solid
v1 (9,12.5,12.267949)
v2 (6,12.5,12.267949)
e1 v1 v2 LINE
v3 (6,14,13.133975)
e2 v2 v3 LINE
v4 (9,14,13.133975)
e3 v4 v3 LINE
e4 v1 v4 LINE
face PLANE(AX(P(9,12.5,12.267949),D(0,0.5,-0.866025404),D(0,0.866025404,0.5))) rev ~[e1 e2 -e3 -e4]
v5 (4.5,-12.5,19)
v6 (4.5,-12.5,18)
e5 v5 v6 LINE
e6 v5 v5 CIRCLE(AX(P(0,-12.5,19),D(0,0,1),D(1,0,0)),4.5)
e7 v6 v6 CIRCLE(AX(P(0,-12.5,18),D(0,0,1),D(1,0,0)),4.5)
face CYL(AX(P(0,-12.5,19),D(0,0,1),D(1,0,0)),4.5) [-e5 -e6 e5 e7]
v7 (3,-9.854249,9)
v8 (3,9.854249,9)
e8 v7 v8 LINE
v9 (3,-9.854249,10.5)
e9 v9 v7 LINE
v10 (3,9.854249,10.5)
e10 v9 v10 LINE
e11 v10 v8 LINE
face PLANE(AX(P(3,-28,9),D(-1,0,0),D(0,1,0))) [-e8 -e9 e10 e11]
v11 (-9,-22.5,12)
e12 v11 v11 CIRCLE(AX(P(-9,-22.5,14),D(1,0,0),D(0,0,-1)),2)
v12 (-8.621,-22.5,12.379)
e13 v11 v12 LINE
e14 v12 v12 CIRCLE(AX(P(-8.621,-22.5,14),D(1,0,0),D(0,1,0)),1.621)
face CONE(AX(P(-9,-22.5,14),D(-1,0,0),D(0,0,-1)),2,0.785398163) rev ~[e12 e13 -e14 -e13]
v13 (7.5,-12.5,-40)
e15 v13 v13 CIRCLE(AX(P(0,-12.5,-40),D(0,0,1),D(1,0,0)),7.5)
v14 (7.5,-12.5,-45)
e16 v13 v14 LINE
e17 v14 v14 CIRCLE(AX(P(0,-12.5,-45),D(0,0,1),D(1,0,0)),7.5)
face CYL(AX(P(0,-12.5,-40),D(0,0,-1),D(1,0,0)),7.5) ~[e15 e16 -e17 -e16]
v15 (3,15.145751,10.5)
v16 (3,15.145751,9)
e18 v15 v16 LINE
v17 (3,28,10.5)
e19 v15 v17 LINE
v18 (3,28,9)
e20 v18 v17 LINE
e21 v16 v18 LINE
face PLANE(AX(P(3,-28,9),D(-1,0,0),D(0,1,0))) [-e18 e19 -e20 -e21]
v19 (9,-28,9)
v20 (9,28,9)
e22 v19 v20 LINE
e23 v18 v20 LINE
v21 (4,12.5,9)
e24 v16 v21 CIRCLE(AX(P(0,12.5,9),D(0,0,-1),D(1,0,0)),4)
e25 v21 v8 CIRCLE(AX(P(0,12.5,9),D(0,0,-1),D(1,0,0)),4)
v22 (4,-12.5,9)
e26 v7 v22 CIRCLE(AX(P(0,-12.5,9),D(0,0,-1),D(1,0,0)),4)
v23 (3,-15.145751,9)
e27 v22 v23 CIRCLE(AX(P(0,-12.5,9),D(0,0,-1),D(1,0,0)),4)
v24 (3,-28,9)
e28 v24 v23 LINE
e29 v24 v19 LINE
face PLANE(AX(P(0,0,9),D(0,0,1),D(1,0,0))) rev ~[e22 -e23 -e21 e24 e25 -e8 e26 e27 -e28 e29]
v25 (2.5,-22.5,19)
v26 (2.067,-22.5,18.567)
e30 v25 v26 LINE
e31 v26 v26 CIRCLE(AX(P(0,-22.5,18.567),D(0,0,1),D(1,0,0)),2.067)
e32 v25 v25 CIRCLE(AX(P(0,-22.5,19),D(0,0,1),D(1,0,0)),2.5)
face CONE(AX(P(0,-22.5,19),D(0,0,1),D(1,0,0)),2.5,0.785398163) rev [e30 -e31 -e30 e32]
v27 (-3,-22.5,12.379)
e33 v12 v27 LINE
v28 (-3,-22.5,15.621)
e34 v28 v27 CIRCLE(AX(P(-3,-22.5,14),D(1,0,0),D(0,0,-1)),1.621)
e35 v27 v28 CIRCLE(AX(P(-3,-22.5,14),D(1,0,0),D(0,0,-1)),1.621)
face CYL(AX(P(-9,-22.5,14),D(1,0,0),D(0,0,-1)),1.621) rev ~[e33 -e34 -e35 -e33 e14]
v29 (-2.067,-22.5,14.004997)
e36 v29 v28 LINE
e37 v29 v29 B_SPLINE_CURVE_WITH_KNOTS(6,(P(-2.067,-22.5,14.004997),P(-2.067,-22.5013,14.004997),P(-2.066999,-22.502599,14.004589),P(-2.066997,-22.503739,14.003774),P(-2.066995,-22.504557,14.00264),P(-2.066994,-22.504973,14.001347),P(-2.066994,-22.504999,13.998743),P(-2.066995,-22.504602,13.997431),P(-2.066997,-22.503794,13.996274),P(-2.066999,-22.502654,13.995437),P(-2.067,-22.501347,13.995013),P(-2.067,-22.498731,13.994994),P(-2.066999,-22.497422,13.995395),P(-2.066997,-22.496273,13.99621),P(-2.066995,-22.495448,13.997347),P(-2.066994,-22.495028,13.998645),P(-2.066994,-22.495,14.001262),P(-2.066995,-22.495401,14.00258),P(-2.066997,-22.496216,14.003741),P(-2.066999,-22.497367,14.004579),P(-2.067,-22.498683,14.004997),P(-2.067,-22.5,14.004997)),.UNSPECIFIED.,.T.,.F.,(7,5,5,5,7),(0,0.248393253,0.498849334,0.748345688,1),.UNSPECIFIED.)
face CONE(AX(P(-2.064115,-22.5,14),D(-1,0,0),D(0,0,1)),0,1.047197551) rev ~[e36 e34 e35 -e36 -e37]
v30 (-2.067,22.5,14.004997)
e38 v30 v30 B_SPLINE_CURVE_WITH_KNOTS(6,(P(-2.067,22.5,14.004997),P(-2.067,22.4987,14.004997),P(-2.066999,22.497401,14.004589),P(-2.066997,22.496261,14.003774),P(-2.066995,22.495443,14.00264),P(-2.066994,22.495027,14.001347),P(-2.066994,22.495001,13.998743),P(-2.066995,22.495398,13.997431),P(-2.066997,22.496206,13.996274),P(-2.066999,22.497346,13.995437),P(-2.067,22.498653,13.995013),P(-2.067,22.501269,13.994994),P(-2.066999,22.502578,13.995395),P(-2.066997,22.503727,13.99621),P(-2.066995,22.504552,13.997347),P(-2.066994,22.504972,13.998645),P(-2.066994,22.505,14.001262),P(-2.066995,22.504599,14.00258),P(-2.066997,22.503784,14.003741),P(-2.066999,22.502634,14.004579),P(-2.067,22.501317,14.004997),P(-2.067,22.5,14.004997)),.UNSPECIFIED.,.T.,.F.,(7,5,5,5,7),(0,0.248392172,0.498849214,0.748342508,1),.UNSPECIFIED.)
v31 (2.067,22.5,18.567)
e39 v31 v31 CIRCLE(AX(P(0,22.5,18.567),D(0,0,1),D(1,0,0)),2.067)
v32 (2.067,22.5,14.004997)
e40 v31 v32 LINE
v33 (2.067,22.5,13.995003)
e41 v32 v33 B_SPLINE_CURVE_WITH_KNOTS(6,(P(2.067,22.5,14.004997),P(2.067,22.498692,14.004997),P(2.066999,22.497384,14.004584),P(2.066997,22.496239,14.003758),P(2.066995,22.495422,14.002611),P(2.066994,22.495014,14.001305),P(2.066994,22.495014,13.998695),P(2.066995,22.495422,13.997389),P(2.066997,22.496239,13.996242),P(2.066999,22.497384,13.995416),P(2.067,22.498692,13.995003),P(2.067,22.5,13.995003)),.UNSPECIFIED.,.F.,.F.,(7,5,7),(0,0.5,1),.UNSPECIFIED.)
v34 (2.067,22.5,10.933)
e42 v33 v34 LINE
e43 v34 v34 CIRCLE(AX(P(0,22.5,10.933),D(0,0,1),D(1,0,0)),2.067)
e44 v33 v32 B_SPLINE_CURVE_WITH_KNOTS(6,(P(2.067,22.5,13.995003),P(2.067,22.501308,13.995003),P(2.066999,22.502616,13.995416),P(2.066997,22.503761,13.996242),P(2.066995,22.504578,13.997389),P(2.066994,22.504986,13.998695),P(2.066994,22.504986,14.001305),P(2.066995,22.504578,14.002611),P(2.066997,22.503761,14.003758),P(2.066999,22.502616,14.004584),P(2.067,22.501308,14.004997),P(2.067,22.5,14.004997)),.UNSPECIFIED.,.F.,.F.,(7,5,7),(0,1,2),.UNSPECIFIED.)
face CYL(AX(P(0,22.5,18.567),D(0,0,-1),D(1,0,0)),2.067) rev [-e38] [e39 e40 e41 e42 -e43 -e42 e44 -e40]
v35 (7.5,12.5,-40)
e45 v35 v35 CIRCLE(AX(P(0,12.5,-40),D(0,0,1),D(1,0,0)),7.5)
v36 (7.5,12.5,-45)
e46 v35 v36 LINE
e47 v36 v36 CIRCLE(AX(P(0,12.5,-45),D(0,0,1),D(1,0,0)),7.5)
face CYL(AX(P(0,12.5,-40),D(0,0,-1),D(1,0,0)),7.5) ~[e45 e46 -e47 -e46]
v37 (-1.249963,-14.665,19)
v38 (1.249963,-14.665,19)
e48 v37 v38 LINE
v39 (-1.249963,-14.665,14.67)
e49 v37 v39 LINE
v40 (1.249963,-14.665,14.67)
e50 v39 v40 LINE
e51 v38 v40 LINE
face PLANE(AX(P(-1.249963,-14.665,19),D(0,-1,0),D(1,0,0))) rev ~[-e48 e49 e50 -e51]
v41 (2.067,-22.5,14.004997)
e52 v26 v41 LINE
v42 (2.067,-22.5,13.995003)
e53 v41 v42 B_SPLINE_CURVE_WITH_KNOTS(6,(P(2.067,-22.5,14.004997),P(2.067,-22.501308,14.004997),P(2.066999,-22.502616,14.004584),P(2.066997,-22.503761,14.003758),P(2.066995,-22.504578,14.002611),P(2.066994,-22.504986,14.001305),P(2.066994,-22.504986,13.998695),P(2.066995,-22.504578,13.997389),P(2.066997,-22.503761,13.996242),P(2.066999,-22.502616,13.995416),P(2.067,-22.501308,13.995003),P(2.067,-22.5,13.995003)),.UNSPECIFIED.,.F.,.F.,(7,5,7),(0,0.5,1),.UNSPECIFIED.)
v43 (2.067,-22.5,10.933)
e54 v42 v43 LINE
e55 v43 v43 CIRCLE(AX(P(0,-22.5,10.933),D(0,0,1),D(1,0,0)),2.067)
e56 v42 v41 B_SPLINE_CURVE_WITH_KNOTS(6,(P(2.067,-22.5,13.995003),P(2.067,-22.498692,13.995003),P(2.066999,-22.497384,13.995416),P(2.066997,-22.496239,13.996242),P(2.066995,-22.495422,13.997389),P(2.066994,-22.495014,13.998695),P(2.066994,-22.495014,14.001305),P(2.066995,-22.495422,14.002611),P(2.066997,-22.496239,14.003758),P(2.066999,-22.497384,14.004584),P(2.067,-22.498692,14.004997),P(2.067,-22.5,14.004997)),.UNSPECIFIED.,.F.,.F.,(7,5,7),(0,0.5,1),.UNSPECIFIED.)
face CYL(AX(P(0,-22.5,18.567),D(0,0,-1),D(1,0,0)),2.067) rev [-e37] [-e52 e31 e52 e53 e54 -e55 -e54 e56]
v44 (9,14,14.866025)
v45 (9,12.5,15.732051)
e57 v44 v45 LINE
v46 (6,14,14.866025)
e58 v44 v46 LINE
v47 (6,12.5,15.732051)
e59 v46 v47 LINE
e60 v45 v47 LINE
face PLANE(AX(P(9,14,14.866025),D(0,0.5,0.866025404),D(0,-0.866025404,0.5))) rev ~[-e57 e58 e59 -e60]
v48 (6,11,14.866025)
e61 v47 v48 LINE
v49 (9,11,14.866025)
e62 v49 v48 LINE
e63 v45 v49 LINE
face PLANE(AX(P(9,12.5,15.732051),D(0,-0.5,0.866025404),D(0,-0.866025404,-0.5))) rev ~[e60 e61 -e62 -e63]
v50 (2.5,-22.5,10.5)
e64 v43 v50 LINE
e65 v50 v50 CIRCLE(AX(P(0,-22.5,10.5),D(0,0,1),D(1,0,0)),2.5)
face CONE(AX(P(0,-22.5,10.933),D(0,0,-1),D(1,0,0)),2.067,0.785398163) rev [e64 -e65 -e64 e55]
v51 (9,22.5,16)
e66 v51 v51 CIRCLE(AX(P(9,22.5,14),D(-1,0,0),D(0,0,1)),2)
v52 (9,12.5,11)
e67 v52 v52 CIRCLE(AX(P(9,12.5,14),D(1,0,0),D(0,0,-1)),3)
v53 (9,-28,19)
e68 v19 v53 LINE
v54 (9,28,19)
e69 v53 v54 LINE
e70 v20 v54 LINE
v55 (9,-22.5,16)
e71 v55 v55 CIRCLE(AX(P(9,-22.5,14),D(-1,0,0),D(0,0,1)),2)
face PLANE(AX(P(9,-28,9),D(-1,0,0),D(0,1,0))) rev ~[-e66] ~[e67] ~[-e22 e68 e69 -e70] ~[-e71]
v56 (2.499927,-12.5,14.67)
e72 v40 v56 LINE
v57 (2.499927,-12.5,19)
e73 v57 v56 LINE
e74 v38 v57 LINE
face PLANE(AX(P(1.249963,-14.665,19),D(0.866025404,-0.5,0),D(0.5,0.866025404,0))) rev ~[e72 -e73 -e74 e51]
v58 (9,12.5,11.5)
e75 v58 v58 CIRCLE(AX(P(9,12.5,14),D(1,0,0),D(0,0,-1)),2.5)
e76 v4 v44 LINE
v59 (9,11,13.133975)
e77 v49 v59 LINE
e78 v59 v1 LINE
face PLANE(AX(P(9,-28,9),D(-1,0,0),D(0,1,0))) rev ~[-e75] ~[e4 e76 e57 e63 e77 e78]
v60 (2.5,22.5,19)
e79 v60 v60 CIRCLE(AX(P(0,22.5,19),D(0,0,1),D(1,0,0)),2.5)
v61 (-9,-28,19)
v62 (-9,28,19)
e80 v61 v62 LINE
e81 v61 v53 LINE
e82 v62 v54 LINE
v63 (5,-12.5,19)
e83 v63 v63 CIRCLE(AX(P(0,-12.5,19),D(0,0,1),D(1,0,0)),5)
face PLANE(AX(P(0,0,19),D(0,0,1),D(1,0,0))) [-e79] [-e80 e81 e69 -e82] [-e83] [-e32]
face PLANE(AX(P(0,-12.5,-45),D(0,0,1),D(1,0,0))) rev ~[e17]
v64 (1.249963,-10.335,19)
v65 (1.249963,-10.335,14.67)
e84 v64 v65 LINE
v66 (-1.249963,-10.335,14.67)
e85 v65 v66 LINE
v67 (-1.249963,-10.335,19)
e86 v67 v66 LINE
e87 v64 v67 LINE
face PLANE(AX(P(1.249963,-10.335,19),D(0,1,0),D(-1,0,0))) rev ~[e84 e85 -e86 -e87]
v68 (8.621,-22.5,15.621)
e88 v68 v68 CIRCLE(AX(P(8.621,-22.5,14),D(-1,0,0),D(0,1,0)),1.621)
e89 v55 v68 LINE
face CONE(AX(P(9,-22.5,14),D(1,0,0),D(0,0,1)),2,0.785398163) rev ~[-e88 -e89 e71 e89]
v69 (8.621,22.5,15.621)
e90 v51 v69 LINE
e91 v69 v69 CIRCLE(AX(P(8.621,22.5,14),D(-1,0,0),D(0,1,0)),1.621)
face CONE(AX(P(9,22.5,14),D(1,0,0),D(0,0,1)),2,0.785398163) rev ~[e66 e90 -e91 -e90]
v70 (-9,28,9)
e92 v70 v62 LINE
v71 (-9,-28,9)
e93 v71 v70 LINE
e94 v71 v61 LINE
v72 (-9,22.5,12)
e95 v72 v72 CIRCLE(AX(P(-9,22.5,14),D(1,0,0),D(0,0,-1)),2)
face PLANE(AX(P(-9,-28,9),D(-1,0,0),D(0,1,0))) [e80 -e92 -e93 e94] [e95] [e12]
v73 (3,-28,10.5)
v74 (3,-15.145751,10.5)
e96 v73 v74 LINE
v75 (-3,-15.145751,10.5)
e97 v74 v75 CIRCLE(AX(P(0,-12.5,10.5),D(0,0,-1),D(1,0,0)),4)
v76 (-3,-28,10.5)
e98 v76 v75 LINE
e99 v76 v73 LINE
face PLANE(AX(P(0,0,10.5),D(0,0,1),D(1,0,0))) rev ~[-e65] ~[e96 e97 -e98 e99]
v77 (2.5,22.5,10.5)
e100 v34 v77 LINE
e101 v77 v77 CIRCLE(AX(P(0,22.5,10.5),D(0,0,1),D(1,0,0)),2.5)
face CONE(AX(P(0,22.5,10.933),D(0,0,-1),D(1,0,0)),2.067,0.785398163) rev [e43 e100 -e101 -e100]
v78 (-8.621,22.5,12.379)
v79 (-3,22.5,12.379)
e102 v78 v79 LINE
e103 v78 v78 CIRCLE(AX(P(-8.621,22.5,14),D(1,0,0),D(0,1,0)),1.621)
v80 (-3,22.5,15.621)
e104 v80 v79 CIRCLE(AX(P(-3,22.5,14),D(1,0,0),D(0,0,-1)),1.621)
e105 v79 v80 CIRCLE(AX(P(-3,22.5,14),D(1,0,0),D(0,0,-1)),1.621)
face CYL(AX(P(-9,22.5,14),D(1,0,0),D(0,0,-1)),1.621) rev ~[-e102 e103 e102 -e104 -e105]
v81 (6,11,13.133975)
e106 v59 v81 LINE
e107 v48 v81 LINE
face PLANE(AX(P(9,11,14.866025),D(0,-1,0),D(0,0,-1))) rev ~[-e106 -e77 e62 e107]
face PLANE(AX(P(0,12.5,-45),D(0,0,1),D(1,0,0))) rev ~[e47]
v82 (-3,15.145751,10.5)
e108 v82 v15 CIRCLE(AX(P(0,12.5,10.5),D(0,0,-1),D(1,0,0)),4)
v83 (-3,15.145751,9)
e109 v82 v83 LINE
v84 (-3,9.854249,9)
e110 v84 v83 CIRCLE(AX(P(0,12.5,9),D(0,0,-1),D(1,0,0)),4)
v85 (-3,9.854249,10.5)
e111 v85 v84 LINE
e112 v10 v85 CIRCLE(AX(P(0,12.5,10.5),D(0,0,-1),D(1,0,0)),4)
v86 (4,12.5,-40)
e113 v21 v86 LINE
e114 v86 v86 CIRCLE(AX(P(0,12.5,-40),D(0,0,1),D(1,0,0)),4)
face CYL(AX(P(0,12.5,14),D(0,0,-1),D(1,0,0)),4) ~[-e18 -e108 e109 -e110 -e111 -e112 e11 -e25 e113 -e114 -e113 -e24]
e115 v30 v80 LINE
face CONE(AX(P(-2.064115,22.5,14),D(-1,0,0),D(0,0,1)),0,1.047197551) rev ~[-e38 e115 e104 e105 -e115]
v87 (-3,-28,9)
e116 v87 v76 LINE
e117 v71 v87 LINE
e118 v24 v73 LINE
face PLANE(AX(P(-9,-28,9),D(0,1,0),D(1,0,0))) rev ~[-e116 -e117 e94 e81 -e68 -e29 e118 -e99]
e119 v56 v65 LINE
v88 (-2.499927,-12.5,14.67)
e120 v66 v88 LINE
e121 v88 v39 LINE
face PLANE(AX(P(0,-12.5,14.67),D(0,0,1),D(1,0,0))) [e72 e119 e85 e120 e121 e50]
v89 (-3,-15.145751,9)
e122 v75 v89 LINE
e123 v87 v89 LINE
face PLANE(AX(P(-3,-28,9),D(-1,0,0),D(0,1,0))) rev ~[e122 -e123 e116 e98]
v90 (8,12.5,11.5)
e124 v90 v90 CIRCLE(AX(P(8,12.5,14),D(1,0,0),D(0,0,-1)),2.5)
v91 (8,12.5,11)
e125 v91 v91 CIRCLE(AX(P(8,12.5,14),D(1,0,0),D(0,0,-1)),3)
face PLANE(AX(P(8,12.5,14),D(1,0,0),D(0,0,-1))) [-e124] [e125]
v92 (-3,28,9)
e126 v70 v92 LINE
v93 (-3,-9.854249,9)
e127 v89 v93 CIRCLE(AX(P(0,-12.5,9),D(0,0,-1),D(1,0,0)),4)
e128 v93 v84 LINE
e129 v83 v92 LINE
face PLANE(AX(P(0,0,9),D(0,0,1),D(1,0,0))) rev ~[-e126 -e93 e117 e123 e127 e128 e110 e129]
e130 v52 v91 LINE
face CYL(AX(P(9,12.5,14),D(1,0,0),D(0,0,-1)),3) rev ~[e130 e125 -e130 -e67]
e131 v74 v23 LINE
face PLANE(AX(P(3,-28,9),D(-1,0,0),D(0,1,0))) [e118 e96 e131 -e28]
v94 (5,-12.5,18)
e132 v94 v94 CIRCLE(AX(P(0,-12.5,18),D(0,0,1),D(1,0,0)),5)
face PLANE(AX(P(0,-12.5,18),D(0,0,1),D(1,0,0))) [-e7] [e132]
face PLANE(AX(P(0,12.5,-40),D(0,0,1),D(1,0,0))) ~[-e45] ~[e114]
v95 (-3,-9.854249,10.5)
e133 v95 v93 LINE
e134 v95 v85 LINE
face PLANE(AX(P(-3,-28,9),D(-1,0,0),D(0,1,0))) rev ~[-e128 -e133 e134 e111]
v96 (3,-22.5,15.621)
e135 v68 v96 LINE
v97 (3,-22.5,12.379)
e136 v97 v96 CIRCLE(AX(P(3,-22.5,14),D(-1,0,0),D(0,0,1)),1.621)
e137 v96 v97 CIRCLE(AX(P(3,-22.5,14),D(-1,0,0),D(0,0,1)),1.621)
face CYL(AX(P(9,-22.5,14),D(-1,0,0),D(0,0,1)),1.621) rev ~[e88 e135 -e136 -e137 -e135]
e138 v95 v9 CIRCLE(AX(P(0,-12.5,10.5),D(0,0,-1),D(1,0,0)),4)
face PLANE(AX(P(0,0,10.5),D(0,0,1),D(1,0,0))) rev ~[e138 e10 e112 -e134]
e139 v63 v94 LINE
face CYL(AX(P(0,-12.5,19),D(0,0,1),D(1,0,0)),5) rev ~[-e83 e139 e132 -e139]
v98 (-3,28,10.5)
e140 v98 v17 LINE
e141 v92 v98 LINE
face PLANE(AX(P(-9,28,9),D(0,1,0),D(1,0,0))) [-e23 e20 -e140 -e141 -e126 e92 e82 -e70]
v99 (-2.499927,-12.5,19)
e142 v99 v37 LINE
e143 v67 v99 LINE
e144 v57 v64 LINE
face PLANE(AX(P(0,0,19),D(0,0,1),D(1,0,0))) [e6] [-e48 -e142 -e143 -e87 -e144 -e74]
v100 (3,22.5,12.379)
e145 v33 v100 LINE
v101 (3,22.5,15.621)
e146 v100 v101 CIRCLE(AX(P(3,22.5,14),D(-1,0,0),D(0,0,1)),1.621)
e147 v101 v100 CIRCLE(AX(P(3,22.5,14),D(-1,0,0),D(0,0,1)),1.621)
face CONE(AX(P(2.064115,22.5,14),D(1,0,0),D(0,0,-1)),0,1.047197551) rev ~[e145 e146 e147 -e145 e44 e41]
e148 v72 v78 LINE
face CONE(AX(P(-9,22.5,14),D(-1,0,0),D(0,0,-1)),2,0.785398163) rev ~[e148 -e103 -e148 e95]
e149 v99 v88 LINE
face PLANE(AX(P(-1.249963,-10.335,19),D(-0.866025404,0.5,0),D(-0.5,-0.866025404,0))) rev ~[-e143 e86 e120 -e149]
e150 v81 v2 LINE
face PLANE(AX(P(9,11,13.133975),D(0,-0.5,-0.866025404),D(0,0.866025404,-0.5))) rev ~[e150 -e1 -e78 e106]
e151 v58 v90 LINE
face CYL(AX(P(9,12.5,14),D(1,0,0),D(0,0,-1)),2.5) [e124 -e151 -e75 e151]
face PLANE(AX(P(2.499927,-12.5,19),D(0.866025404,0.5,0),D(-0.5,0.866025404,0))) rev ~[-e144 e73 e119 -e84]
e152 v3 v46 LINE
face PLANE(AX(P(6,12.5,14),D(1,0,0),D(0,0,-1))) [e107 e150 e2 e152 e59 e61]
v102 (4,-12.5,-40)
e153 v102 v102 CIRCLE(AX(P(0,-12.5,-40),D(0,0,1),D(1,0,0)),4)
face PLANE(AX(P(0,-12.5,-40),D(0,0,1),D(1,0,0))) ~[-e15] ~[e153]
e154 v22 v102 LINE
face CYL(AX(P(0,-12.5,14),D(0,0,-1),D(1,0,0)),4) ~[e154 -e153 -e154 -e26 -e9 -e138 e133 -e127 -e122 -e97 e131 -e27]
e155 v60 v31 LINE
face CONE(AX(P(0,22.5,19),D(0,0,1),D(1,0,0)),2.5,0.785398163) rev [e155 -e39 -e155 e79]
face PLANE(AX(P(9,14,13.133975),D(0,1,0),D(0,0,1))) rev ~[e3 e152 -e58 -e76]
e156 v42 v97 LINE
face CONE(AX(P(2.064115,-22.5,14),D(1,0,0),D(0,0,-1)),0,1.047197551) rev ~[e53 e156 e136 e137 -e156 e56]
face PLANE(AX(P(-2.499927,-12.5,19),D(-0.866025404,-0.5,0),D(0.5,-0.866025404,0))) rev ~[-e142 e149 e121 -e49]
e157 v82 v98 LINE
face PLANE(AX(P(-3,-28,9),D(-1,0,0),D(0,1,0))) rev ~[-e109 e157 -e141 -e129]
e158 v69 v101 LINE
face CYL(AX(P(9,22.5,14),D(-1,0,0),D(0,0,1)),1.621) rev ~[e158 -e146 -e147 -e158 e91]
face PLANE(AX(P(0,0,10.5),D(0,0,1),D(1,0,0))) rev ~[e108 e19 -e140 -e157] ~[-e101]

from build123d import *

# Parameters (mm, degrees)
SKETCH1_W           = 18
SKETCH1_H           = 56
BOSS_EXTRUDE1_DEPTH = 10
SKETCH2_W           = 6
SKETCH2_H           = 56
CUT_EXTRUDE1_DEPTH  = 1.5
HOLE1_D             = 3.242
HOLE1_DEPTH         = 6
HOLE1_CSINK_D       = 4
HOLE1_CSINK_ANGLE   = 90
HOLE1_TIP           = 0.935884786
HOLE2_D             = 3.242
HOLE2_DEPTH         = 6
HOLE2_CSINK_D       = 4
HOLE2_CSINK_ANGLE   = 90
HOLE2_TIP           = 0.935884786
HOLE3_D             = 3.242
HOLE3_DEPTH         = 6
HOLE3_CSINK_D       = 4
HOLE3_CSINK_ANGLE   = 90
HOLE3_TIP           = 0.935884786
HOLE4_D             = 3.242
HOLE4_DEPTH         = 6
HOLE4_CSINK_D       = 4
HOLE4_CSINK_ANGLE   = 90
HOLE4_TIP           = 0.935884786
SKETCH15_R          = 5
SKETCH15_R_2        = 4.5
CUT_EXTRUDE2_DEPTH  = 1
CUT_EXTRUDE3_DEPTH  = 4.33
SKETCH17_R          = 3
SKETCH17_R_2        = 2.5
CUT_EXTRUDE4_DEPTH  = 1
CUT_EXTRUDE5_DEPTH  = 3


with BuildPart() as part:
    # Sketch1 → Boss-Extrude1 (new body)
    with BuildSketch(Plane.XY.offset(9)):
        Rectangle(SKETCH1_W, SKETCH1_H)
    extrude(amount=BOSS_EXTRUDE1_DEPTH)

    # Sketch2 → Cut-Extrude1 (cut)
    with BuildSketch(Plane.XY.offset(9)):
        Rectangle(SKETCH2_W, SKETCH2_H)
    extrude(amount=CUT_EXTRUDE1_DEPTH, mode=Mode.SUBTRACT)

    # Sketch3 → Revolve1 (revolve)
    with BuildSketch(Plane(origin=(0, 0, 0), x_dir=(0, 0, -1), z_dir=(1, 0, 0)), mode=Mode.PRIVATE) as revolve1_sk:
        Polygon((-14, 12.5), (-14, 16.5), (40, 16.5), (40, 20), (45, 20), (45, 12.5), align=None)
    revolve(revolve1_sk.sketch.rotate(Axis((0, 12.5, -45), (0, 0, 1)), 270), axis=Axis((0, 12.5, -45), (0, 0, 1)))

    # Sketch4 → Revolve2 (revolve)
    with BuildSketch(Plane(origin=(0, 0, 0), x_dir=(0, 0, -1), z_dir=(1, 0, 0)), mode=Mode.PRIVATE) as revolve2_sk:
        Polygon((-14, -12.5), (-14, -8.5), (40, -8.5), (40, -5), (45, -5), (45, -12.5), align=None)
    revolve(revolve2_sk.sketch.rotate(Axis((0, -12.5, -45), (0, 0, 1)), 270), axis=Axis((0, -12.5, -45), (0, 0, 1)))

    # Sketch5 → Cut-Revolve1 (revolve, cut)
    with BuildSketch(Plane(origin=(0, 0, 0), x_dir=(0, 0, -1), z_dir=(1, 0, 0)), mode=Mode.PRIVATE) as cut_revolve1_sk:
        Polygon((-19, 22.5), (-19, 25), (-18.567, 24.567), (-10.933, 24.567), (-10.5, 25), (-10.5, 22.5), align=None)
    revolve(cut_revolve1_sk.sketch.rotate(Axis((0, 22.5, 10.5), (0, 0, 1)), 270), axis=Axis((0, 22.5, 10.5), (0, 0, 1)), mode=Mode.SUBTRACT)

    # Sketch6 → Cut-Revolve2 (revolve, cut)
    with BuildSketch(Plane(origin=(0, 0, 0), x_dir=(0, 0, -1), z_dir=(1, 0, 0)), mode=Mode.PRIVATE) as cut_revolve2_sk:
        Polygon((-19, -22.5), (-19, -20), (-18.567, -20.433), (-10.933, -20.433), (-10.5, -20), (-10.5, -22.5), align=None)
    revolve(cut_revolve2_sk.sketch.rotate(Axis((0, -22.5, 10.5), (0, 0, 1)), 270), axis=Axis((0, -22.5, 10.5), (0, 0, 1)), mode=Mode.SUBTRACT)

    # Hole1
    with Locations(Plane.ZY.offset(9)):
        with Locations((14, 22.5)):
            CounterSinkHole(HOLE1_D / 2, HOLE1_CSINK_D / 2, depth=HOLE1_DEPTH, counter_sink_angle=HOLE1_CSINK_ANGLE)
            with Locations((0, 0, -(HOLE1_DEPTH + HOLE1_TIP / 2))):  # 120° drill point
                Cone(0, HOLE1_D / 2, HOLE1_TIP, mode=Mode.SUBTRACT)

    # Hole2
    with Locations(Plane.ZY.offset(9)):
        with Locations((14, -22.5)):
            CounterSinkHole(HOLE2_D / 2, HOLE2_CSINK_D / 2, depth=HOLE2_DEPTH, counter_sink_angle=HOLE2_CSINK_ANGLE)
            with Locations((0, 0, -(HOLE2_DEPTH + HOLE2_TIP / 2))):  # 120° drill point
                Cone(0, HOLE2_D / 2, HOLE2_TIP, mode=Mode.SUBTRACT)

    # Hole3
    with Locations(Plane(origin=(9, 0, 0), x_dir=(0, 0, -1), z_dir=(1, 0, 0))):
        with Locations((-14, 22.5)):
            CounterSinkHole(HOLE3_D / 2, HOLE3_CSINK_D / 2, depth=HOLE3_DEPTH, counter_sink_angle=HOLE3_CSINK_ANGLE)
            with Locations((0, 0, -(HOLE3_DEPTH + HOLE3_TIP / 2))):  # 120° drill point
                Cone(0, HOLE3_D / 2, HOLE3_TIP, mode=Mode.SUBTRACT)

    # Hole4
    with Locations(Plane(origin=(9, 0, 0), x_dir=(0, 0, -1), z_dir=(1, 0, 0))):
        with Locations((-14, -22.5)):
            CounterSinkHole(HOLE4_D / 2, HOLE4_CSINK_D / 2, depth=HOLE4_DEPTH, counter_sink_angle=HOLE4_CSINK_ANGLE)
            with Locations((0, 0, -(HOLE4_DEPTH + HOLE4_TIP / 2))):  # 120° drill point
                Cone(0, HOLE4_D / 2, HOLE4_TIP, mode=Mode.SUBTRACT)

    # Sketch15 → Cut-Extrude2 (cut)
    with BuildSketch(Plane.XY.offset(19)):
        with Locations((0, -12.5)):
            Circle(SKETCH15_R)
        with Locations((0, -12.5)):
            Circle(SKETCH15_R_2, mode=Mode.SUBTRACT)
    extrude(amount=-CUT_EXTRUDE2_DEPTH, mode=Mode.SUBTRACT)

    # Sketch16 → Cut-Extrude3 (cut)
    with BuildSketch(Plane.XY.offset(19)):
        Polygon((-2.499926666, -12.5), (-1.249963333, -14.665), (1.249963333, -14.665), (2.499926666, -12.5), (1.249963333, -10.335), (-1.249963333, -10.335), align=None)
    extrude(amount=-CUT_EXTRUDE3_DEPTH, mode=Mode.SUBTRACT)

    # Sketch17 → Cut-Extrude4 (cut)
    with BuildSketch(Plane(origin=(9, 0, 0), x_dir=(0, 0, -1), z_dir=(1, 0, 0))):
        with Locations((-14, 12.5)):
            Circle(SKETCH17_R)
        with Locations((-14, 12.5)):
            Circle(SKETCH17_R_2, mode=Mode.SUBTRACT)
    extrude(amount=-CUT_EXTRUDE4_DEPTH, mode=Mode.SUBTRACT)

    # Sketch18 → Cut-Extrude5 (cut)
    with BuildSketch(Plane(origin=(9, 0, 0), x_dir=(0, 0, -1), z_dir=(1, 0, 0))):
        Polygon((-15.732050808, 12.5), (-14.866025404, 11), (-13.133974596, 11), (-12.267949192, 12.5), (-13.133974596, 14), (-14.866025404, 14), align=None)
    extrude(amount=-CUT_EXTRUDE5_DEPTH, mode=Mode.SUBTRACT)


solid = part.part
